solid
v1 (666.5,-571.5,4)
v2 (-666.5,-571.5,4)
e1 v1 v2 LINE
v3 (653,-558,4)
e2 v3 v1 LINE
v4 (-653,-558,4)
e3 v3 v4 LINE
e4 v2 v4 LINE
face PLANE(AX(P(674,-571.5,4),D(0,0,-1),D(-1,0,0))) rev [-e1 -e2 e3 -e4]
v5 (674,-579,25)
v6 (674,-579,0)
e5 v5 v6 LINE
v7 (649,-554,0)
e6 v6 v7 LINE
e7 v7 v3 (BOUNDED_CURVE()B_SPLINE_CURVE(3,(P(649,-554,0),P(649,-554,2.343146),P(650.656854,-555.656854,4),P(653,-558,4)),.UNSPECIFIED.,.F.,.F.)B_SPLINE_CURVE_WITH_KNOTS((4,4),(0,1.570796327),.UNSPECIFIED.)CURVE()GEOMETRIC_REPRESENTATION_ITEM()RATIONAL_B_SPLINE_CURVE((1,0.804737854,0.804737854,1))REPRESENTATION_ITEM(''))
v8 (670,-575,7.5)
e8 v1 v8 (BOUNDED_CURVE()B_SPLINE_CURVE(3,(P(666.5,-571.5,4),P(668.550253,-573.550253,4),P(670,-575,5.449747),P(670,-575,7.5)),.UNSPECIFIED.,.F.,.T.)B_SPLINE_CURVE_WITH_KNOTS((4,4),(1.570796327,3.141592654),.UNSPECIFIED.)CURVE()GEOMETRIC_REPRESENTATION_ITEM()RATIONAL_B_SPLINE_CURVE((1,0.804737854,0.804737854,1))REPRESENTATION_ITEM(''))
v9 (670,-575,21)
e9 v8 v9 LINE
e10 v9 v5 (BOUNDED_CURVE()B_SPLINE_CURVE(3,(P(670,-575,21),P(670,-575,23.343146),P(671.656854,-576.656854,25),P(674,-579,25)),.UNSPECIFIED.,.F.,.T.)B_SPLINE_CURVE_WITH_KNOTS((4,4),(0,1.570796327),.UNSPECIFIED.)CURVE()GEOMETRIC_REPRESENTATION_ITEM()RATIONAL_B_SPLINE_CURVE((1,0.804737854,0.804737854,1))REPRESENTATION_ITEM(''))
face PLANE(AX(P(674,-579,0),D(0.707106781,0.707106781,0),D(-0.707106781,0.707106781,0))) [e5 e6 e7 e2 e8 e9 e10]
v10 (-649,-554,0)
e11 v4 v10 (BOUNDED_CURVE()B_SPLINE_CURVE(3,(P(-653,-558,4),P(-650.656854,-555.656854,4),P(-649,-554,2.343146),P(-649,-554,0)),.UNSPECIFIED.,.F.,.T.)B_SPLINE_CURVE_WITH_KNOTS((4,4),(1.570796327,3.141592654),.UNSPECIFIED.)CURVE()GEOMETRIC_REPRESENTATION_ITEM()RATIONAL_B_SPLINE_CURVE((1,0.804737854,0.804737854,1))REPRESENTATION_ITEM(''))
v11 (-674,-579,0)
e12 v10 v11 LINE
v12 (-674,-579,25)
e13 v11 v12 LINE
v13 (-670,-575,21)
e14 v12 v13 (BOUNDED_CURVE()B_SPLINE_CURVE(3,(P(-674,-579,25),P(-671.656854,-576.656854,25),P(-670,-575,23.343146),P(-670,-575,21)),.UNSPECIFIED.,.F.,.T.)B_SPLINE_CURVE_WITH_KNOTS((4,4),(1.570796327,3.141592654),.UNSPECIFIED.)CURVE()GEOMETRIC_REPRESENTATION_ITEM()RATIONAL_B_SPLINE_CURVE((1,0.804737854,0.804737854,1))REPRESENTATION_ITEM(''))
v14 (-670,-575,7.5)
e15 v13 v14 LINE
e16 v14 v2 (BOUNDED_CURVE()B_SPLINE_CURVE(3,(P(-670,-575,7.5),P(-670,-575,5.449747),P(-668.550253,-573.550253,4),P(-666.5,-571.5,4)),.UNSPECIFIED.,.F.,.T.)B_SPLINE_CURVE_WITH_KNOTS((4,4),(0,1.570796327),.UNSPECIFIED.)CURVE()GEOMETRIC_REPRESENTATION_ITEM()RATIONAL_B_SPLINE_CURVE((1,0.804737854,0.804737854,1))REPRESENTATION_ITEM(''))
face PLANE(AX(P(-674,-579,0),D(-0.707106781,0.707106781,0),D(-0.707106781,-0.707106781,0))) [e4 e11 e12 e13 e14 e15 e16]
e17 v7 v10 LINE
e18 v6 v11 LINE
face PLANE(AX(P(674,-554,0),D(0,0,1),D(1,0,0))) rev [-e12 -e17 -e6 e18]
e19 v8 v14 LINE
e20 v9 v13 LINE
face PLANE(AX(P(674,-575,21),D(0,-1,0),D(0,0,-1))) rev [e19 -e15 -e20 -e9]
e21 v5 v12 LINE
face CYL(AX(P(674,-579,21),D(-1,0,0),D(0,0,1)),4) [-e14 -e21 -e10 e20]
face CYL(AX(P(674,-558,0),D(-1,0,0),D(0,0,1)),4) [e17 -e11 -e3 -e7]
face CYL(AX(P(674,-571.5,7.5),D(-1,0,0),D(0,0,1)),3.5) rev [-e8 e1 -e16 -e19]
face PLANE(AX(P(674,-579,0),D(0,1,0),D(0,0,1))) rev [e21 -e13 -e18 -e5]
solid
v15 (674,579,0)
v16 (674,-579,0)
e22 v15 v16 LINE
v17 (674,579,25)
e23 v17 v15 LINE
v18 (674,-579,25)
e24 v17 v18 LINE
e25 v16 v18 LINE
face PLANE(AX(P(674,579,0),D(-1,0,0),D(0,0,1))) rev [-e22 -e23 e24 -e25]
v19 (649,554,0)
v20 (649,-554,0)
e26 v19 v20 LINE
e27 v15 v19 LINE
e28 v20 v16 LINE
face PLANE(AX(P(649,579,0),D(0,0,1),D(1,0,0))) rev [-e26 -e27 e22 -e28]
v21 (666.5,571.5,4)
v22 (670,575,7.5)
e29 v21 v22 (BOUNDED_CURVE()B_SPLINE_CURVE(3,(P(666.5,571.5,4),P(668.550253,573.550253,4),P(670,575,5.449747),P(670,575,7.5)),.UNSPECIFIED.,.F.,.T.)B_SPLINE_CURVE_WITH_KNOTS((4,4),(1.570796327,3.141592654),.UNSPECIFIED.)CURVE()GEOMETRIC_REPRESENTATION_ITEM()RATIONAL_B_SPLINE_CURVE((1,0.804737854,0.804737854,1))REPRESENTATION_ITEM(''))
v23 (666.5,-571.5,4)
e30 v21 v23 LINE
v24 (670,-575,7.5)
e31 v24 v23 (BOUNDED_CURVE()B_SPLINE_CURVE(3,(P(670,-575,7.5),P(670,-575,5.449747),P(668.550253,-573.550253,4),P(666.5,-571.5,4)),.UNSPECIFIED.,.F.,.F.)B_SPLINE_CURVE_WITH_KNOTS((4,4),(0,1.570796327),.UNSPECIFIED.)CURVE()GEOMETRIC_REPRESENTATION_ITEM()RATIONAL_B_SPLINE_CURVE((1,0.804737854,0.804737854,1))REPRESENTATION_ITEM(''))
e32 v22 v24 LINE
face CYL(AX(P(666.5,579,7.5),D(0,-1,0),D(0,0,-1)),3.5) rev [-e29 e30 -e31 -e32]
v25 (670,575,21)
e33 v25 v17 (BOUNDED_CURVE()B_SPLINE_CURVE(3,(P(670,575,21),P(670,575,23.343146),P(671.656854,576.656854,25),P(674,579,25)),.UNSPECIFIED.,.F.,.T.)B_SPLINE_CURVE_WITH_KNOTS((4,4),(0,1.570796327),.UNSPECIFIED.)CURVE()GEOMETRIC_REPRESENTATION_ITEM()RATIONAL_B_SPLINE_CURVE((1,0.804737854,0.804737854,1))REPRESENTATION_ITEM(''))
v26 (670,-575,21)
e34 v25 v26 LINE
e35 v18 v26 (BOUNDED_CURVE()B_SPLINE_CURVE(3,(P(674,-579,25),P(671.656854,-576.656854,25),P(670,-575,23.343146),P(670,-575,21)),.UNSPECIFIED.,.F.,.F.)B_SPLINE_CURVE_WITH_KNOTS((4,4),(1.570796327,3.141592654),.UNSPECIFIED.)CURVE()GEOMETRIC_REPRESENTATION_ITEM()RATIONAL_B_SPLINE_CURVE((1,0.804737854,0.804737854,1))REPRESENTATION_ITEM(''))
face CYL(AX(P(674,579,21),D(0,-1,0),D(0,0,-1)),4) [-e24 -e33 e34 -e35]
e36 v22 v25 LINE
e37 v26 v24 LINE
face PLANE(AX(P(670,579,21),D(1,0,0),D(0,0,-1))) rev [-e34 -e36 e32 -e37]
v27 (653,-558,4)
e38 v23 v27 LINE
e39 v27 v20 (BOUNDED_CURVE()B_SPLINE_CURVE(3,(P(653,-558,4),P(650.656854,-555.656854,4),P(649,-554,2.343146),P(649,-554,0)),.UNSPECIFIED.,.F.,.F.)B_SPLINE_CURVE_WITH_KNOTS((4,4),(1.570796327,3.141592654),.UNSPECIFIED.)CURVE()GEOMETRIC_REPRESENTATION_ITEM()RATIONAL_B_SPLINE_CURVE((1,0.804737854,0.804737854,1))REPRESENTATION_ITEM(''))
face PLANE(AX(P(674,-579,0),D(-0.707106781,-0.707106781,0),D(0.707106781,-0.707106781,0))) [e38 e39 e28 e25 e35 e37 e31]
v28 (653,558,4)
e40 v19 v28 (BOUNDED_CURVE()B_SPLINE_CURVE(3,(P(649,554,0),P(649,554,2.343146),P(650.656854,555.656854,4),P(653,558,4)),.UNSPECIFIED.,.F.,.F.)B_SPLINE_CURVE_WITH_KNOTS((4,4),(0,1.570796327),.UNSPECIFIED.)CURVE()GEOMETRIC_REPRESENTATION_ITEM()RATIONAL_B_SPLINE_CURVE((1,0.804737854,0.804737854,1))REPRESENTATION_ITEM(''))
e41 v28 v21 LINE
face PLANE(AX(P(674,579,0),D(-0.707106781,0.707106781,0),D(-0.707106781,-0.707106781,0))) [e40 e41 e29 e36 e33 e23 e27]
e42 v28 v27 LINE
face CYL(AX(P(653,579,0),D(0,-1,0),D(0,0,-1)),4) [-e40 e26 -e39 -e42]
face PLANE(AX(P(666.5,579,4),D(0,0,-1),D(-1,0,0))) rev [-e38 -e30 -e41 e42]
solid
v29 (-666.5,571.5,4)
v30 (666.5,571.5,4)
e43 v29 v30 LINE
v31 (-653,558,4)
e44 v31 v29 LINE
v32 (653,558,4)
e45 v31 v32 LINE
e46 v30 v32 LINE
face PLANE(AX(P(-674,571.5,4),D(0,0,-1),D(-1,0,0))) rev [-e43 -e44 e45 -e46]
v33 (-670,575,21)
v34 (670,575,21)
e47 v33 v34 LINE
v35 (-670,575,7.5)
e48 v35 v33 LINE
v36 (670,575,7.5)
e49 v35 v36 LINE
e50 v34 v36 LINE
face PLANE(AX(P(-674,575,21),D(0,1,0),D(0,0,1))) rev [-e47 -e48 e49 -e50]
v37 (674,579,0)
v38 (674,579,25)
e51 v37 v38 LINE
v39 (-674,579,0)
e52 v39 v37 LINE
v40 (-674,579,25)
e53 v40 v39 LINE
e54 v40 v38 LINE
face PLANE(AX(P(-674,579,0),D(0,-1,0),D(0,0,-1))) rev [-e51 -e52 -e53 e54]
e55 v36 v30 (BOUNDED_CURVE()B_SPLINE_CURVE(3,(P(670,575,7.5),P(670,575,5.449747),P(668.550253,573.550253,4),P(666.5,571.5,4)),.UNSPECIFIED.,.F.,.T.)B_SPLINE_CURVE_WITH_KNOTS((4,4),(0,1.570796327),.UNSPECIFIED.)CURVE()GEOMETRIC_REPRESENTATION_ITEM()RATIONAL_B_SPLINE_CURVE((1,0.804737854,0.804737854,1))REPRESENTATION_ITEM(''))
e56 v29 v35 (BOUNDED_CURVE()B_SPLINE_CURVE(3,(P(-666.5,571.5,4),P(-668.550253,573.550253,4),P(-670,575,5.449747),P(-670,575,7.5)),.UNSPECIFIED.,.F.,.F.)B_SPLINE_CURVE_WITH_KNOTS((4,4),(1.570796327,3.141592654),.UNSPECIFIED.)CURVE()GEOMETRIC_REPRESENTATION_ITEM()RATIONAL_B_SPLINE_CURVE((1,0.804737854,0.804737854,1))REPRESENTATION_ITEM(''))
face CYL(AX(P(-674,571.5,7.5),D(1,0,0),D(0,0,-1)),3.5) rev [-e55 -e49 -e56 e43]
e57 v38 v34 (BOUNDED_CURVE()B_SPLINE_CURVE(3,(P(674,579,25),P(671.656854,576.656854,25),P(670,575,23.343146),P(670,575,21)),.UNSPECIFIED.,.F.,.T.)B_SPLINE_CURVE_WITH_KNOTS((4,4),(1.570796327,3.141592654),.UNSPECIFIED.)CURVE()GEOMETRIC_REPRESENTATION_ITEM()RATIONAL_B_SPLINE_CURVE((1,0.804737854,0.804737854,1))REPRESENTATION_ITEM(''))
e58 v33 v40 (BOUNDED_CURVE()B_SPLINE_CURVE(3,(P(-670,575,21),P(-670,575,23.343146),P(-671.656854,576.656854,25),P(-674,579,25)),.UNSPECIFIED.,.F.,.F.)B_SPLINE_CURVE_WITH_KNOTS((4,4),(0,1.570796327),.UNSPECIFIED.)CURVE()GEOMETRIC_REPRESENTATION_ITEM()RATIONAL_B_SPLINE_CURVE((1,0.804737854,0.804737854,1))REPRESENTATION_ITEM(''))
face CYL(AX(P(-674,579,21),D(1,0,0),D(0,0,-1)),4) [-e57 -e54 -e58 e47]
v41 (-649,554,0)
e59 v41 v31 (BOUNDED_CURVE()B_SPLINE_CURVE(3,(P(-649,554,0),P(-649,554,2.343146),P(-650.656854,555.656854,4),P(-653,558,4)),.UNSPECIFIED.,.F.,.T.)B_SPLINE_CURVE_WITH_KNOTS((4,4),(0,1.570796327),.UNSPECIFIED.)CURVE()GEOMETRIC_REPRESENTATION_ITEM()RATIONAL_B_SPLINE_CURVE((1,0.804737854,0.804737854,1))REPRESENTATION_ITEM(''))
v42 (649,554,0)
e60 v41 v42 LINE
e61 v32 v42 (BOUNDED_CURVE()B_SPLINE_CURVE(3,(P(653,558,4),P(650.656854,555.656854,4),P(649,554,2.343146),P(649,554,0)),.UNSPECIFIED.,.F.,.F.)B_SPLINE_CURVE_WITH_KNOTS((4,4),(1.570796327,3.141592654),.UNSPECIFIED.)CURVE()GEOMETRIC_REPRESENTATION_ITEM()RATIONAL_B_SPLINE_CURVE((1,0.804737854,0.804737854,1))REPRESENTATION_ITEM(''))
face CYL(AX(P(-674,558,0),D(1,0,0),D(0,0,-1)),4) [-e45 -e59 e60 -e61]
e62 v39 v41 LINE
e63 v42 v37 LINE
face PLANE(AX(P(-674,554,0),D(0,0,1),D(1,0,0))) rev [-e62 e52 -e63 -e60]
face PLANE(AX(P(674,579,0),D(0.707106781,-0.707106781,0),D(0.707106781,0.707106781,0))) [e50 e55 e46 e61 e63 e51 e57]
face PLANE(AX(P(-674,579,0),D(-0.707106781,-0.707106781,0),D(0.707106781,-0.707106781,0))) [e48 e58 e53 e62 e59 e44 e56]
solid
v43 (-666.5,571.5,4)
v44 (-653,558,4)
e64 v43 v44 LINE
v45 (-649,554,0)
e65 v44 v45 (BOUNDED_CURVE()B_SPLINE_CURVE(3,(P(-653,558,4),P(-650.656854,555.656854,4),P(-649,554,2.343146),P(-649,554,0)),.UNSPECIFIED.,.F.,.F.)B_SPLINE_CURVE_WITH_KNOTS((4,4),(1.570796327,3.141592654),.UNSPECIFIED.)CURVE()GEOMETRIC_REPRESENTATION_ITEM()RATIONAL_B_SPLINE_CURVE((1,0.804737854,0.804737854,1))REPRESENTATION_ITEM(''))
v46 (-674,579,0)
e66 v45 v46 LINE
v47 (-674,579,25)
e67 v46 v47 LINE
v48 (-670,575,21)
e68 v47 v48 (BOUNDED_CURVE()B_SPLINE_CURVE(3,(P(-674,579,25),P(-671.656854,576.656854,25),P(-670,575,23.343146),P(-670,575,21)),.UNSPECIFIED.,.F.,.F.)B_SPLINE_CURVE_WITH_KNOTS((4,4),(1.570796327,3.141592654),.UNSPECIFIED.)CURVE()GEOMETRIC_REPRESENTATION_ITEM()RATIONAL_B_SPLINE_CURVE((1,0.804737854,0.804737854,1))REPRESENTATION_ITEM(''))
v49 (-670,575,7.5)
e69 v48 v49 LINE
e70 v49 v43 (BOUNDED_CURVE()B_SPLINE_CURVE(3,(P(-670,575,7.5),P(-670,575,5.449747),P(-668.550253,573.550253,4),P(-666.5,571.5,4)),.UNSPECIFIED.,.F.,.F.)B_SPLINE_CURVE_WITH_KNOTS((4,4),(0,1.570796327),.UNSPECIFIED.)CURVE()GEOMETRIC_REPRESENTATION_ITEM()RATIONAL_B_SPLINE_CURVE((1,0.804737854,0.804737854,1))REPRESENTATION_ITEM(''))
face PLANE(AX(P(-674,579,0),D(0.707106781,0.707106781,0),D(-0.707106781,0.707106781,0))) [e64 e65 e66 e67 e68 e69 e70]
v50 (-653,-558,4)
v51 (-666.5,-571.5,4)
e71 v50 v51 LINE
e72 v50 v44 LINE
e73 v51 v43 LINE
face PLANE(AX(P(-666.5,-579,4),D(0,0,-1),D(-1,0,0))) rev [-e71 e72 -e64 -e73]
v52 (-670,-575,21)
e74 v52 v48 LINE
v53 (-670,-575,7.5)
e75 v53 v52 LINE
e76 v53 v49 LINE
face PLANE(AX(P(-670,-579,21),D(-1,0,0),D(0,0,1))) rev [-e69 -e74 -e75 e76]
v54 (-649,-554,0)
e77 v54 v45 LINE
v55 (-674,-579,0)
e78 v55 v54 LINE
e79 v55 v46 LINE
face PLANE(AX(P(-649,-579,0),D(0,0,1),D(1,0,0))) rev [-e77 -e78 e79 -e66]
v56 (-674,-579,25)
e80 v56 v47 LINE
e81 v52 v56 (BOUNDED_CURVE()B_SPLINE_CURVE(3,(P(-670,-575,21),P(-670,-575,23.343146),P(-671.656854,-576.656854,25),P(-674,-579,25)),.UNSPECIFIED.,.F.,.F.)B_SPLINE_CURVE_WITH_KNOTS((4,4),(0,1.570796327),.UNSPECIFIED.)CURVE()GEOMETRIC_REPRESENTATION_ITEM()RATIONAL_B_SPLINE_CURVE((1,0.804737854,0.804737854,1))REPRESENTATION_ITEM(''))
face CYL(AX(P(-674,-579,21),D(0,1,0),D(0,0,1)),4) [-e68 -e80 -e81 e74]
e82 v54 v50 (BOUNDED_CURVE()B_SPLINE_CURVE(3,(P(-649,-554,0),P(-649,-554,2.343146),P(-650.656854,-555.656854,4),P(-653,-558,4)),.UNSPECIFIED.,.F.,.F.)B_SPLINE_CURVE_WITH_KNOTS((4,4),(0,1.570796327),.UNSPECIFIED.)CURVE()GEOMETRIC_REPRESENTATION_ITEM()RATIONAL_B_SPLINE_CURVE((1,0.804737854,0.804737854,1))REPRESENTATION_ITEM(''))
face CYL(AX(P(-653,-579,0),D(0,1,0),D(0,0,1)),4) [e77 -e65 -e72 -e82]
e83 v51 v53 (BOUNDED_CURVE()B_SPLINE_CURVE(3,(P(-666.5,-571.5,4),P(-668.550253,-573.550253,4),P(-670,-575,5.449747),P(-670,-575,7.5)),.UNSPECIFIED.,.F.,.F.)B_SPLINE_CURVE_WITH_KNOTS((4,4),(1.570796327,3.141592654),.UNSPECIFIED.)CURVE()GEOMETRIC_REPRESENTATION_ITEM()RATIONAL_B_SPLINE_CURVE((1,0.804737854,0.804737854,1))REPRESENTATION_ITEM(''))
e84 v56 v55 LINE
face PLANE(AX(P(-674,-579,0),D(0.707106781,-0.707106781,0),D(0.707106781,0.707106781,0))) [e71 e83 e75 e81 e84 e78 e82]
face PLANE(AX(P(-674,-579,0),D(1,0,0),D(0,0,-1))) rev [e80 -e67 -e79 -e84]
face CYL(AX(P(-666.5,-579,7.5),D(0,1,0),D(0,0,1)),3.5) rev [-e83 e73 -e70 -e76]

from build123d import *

# Parameters (mm, degrees)
ANGLE_IRON_CONFIGURED_25_X_25_X_4_1_DEPTH      = 1194.355339059
ANGLE_IRON_CONFIGURED_25_X_25_X_4_1_DEPTH_BACK = 36.355339059
ANGLE_IRON_CONFIGURED_25_X_25_X_4_1_2_DEPTH    = 1420.710678119
ANGLE_IRON_CONFIGURED_25_X_25_X_4_1_3_DEPTH    = 1230.710678119
ANGLE_IRON_CONFIGURED_25_X_25_X_4_1_4_DEPTH    = 1420.710678119


with BuildPart() as part:
    # Sketch1 → Angle iron - configured 25 X 25 X 4(1) (new, two sides: drawn at the far end of the back side and taken through both)
    with BuildSketch(Plane(origin=(-674, 579, 0), x_dir=(1, 0, 0), z_dir=(0, -1, 0)).offset(-ANGLE_IRON_CONFIGURED_25_X_25_X_4_1_DEPTH_BACK)):
        with BuildLine():
            Line((0, 0), (0, 25))
            ThreePointArc((0, 25), (2.828427125, 23.828427125), (4, 21))
            Line((4, 21), (4, 7.5))
            ThreePointArc((4, 7.5), (5.025126266, 5.025126266), (7.5, 4))
            Line((7.5, 4), (21, 4))
            ThreePointArc((21, 4), (23.828427125, 2.828427125), (25, 0))
            Line((25, 0), (0, 0))
        make_face()
    extrude(amount=ANGLE_IRON_CONFIGURED_25_X_25_X_4_1_DEPTH + ANGLE_IRON_CONFIGURED_25_X_25_X_4_1_DEPTH_BACK)

    # Angle iron - configured 25 X 25 X 4(1) mi
    split(bisect_by=Plane(origin=(-674, 579, 0), x_dir=(0.707106781, -0.707106781, 0), z_dir=(-0.707106781, -0.707106781, 0)), keep=Keep.TOP)

    # Angle iron - configured 25 X 25 X 4_ 2
    split(bisect_by=Plane(origin=(-674, -579, 0), x_dir=(-0.707106781, -0.707106781, 0), z_dir=(-0.707106781, 0.707106781, 0)), keep=Keep.TOP)


with BuildPart() as body_2:
    # Sketch1 on segment 2 (carried to segment 2) → Angle iron - configured 25 X 25 X 4_1 2 (new body)
    with BuildSketch(Plane(origin=(-710.355339059, -579, 0), x_dir=(0, 1, 0), z_dir=(1, 0, 0))):
        with BuildLine():
            Line((0, 0), (0, 25))
            ThreePointArc((0, 25), (2.828427125, 23.828427125), (4, 21))
            Line((4, 21), (4, 7.5))
            ThreePointArc((4, 7.5), (5.025126266, 5.025126266), (7.5, 4))
            Line((7.5, 4), (21, 4))
            ThreePointArc((21, 4), (23.828427125, 2.828427125), (25, 0))
            Line((25, 0), (0, 0))
        make_face()
    extrude(amount=ANGLE_IRON_CONFIGURED_25_X_25_X_4_1_2_DEPTH)

    # Angle iron - configured 25 X 25 X 4_ 3
    split(bisect_by=Plane(origin=(-674, -579, 0), x_dir=(0.707106781, 0.707106781, 0), z_dir=(0.707106781, -0.707106781, 0)), keep=Keep.TOP)

    # Angle iron - configured 25 X 25 X 4_ 4
    split(bisect_by=Plane(origin=(674, -579, 0), x_dir=(0.707106781, -0.707106781, 0), z_dir=(-0.707106781, -0.707106781, 0)), keep=Keep.TOP)


with BuildPart() as body_3:
    # Sketch1 on segment 3 (carried to segment 3) → Angle iron - configured 25 X 25 X 4_1 3 (new body)
    with BuildSketch(Plane(origin=(674, -615.355339059, 0), x_dir=(-1, 0, 0), z_dir=(0, 1, 0))):
        with BuildLine():
            Line((0, 0), (0, 25))
            ThreePointArc((0, 25), (2.828427125, 23.828427125), (4, 21))
            Line((4, 21), (4, 7.5))
            ThreePointArc((4, 7.5), (5.025126266, 5.025126266), (7.5, 4))
            Line((7.5, 4), (21, 4))
            ThreePointArc((21, 4), (23.828427125, 2.828427125), (25, 0))
            Line((25, 0), (0, 0))
        make_face()
    extrude(amount=ANGLE_IRON_CONFIGURED_25_X_25_X_4_1_3_DEPTH)

    # Angle iron - configured 25 X 25 X 4_ 5
    split(bisect_by=Plane(origin=(674, 579, 0), x_dir=(0.707106781, 0.707106781, 0), z_dir=(0.707106781, -0.707106781, 0)), keep=Keep.TOP)

    # Angle iron - configured 25 X 25 X 4_ 6
    split(bisect_by=Plane(origin=(674, -579, 0), x_dir=(-0.707106781, 0.707106781, 0), z_dir=(0.707106781, 0.707106781, 0)), keep=Keep.TOP)


with BuildPart() as body_4:
    # Sketch1 on segment 4 (carried to segment 4) → Angle iron - configured 25 X 25 X 4_1 4 (new body)
    with BuildSketch(Plane(origin=(710.355339059, 579, 0), x_dir=(0, -1, 0), z_dir=(-1, 0, 0))):
        with BuildLine():
            Line((0, 0), (0, 25))
            ThreePointArc((0, 25), (2.828427125, 23.828427125), (4, 21))
            Line((4, 21), (4, 7.5))
            ThreePointArc((4, 7.5), (5.025126266, 5.025126266), (7.5, 4))
            Line((7.5, 4), (21, 4))
            ThreePointArc((21, 4), (23.828427125, 2.828427125), (25, 0))
            Line((25, 0), (0, 0))
        make_face()
    extrude(amount=ANGLE_IRON_CONFIGURED_25_X_25_X_4_1_4_DEPTH)

    # Angle iron - configured 25 X 25 X 4_ 7
    split(bisect_by=Plane(origin=(-674, 579, 0), x_dir=(-0.707106781, 0.707106781, 0), z_dir=(0.707106781, 0.707106781, 0)), keep=Keep.TOP)

    # Angle iron - configured 25 X 25 X 4_ 8
    split(bisect_by=Plane(origin=(674, 579, 0), x_dir=(-0.707106781, -0.707106781, 0), z_dir=(-0.707106781, 0.707106781, 0)), keep=Keep.TOP)


solid = Compound([part.part, body_2.part, body_3.part, body_4.part])
